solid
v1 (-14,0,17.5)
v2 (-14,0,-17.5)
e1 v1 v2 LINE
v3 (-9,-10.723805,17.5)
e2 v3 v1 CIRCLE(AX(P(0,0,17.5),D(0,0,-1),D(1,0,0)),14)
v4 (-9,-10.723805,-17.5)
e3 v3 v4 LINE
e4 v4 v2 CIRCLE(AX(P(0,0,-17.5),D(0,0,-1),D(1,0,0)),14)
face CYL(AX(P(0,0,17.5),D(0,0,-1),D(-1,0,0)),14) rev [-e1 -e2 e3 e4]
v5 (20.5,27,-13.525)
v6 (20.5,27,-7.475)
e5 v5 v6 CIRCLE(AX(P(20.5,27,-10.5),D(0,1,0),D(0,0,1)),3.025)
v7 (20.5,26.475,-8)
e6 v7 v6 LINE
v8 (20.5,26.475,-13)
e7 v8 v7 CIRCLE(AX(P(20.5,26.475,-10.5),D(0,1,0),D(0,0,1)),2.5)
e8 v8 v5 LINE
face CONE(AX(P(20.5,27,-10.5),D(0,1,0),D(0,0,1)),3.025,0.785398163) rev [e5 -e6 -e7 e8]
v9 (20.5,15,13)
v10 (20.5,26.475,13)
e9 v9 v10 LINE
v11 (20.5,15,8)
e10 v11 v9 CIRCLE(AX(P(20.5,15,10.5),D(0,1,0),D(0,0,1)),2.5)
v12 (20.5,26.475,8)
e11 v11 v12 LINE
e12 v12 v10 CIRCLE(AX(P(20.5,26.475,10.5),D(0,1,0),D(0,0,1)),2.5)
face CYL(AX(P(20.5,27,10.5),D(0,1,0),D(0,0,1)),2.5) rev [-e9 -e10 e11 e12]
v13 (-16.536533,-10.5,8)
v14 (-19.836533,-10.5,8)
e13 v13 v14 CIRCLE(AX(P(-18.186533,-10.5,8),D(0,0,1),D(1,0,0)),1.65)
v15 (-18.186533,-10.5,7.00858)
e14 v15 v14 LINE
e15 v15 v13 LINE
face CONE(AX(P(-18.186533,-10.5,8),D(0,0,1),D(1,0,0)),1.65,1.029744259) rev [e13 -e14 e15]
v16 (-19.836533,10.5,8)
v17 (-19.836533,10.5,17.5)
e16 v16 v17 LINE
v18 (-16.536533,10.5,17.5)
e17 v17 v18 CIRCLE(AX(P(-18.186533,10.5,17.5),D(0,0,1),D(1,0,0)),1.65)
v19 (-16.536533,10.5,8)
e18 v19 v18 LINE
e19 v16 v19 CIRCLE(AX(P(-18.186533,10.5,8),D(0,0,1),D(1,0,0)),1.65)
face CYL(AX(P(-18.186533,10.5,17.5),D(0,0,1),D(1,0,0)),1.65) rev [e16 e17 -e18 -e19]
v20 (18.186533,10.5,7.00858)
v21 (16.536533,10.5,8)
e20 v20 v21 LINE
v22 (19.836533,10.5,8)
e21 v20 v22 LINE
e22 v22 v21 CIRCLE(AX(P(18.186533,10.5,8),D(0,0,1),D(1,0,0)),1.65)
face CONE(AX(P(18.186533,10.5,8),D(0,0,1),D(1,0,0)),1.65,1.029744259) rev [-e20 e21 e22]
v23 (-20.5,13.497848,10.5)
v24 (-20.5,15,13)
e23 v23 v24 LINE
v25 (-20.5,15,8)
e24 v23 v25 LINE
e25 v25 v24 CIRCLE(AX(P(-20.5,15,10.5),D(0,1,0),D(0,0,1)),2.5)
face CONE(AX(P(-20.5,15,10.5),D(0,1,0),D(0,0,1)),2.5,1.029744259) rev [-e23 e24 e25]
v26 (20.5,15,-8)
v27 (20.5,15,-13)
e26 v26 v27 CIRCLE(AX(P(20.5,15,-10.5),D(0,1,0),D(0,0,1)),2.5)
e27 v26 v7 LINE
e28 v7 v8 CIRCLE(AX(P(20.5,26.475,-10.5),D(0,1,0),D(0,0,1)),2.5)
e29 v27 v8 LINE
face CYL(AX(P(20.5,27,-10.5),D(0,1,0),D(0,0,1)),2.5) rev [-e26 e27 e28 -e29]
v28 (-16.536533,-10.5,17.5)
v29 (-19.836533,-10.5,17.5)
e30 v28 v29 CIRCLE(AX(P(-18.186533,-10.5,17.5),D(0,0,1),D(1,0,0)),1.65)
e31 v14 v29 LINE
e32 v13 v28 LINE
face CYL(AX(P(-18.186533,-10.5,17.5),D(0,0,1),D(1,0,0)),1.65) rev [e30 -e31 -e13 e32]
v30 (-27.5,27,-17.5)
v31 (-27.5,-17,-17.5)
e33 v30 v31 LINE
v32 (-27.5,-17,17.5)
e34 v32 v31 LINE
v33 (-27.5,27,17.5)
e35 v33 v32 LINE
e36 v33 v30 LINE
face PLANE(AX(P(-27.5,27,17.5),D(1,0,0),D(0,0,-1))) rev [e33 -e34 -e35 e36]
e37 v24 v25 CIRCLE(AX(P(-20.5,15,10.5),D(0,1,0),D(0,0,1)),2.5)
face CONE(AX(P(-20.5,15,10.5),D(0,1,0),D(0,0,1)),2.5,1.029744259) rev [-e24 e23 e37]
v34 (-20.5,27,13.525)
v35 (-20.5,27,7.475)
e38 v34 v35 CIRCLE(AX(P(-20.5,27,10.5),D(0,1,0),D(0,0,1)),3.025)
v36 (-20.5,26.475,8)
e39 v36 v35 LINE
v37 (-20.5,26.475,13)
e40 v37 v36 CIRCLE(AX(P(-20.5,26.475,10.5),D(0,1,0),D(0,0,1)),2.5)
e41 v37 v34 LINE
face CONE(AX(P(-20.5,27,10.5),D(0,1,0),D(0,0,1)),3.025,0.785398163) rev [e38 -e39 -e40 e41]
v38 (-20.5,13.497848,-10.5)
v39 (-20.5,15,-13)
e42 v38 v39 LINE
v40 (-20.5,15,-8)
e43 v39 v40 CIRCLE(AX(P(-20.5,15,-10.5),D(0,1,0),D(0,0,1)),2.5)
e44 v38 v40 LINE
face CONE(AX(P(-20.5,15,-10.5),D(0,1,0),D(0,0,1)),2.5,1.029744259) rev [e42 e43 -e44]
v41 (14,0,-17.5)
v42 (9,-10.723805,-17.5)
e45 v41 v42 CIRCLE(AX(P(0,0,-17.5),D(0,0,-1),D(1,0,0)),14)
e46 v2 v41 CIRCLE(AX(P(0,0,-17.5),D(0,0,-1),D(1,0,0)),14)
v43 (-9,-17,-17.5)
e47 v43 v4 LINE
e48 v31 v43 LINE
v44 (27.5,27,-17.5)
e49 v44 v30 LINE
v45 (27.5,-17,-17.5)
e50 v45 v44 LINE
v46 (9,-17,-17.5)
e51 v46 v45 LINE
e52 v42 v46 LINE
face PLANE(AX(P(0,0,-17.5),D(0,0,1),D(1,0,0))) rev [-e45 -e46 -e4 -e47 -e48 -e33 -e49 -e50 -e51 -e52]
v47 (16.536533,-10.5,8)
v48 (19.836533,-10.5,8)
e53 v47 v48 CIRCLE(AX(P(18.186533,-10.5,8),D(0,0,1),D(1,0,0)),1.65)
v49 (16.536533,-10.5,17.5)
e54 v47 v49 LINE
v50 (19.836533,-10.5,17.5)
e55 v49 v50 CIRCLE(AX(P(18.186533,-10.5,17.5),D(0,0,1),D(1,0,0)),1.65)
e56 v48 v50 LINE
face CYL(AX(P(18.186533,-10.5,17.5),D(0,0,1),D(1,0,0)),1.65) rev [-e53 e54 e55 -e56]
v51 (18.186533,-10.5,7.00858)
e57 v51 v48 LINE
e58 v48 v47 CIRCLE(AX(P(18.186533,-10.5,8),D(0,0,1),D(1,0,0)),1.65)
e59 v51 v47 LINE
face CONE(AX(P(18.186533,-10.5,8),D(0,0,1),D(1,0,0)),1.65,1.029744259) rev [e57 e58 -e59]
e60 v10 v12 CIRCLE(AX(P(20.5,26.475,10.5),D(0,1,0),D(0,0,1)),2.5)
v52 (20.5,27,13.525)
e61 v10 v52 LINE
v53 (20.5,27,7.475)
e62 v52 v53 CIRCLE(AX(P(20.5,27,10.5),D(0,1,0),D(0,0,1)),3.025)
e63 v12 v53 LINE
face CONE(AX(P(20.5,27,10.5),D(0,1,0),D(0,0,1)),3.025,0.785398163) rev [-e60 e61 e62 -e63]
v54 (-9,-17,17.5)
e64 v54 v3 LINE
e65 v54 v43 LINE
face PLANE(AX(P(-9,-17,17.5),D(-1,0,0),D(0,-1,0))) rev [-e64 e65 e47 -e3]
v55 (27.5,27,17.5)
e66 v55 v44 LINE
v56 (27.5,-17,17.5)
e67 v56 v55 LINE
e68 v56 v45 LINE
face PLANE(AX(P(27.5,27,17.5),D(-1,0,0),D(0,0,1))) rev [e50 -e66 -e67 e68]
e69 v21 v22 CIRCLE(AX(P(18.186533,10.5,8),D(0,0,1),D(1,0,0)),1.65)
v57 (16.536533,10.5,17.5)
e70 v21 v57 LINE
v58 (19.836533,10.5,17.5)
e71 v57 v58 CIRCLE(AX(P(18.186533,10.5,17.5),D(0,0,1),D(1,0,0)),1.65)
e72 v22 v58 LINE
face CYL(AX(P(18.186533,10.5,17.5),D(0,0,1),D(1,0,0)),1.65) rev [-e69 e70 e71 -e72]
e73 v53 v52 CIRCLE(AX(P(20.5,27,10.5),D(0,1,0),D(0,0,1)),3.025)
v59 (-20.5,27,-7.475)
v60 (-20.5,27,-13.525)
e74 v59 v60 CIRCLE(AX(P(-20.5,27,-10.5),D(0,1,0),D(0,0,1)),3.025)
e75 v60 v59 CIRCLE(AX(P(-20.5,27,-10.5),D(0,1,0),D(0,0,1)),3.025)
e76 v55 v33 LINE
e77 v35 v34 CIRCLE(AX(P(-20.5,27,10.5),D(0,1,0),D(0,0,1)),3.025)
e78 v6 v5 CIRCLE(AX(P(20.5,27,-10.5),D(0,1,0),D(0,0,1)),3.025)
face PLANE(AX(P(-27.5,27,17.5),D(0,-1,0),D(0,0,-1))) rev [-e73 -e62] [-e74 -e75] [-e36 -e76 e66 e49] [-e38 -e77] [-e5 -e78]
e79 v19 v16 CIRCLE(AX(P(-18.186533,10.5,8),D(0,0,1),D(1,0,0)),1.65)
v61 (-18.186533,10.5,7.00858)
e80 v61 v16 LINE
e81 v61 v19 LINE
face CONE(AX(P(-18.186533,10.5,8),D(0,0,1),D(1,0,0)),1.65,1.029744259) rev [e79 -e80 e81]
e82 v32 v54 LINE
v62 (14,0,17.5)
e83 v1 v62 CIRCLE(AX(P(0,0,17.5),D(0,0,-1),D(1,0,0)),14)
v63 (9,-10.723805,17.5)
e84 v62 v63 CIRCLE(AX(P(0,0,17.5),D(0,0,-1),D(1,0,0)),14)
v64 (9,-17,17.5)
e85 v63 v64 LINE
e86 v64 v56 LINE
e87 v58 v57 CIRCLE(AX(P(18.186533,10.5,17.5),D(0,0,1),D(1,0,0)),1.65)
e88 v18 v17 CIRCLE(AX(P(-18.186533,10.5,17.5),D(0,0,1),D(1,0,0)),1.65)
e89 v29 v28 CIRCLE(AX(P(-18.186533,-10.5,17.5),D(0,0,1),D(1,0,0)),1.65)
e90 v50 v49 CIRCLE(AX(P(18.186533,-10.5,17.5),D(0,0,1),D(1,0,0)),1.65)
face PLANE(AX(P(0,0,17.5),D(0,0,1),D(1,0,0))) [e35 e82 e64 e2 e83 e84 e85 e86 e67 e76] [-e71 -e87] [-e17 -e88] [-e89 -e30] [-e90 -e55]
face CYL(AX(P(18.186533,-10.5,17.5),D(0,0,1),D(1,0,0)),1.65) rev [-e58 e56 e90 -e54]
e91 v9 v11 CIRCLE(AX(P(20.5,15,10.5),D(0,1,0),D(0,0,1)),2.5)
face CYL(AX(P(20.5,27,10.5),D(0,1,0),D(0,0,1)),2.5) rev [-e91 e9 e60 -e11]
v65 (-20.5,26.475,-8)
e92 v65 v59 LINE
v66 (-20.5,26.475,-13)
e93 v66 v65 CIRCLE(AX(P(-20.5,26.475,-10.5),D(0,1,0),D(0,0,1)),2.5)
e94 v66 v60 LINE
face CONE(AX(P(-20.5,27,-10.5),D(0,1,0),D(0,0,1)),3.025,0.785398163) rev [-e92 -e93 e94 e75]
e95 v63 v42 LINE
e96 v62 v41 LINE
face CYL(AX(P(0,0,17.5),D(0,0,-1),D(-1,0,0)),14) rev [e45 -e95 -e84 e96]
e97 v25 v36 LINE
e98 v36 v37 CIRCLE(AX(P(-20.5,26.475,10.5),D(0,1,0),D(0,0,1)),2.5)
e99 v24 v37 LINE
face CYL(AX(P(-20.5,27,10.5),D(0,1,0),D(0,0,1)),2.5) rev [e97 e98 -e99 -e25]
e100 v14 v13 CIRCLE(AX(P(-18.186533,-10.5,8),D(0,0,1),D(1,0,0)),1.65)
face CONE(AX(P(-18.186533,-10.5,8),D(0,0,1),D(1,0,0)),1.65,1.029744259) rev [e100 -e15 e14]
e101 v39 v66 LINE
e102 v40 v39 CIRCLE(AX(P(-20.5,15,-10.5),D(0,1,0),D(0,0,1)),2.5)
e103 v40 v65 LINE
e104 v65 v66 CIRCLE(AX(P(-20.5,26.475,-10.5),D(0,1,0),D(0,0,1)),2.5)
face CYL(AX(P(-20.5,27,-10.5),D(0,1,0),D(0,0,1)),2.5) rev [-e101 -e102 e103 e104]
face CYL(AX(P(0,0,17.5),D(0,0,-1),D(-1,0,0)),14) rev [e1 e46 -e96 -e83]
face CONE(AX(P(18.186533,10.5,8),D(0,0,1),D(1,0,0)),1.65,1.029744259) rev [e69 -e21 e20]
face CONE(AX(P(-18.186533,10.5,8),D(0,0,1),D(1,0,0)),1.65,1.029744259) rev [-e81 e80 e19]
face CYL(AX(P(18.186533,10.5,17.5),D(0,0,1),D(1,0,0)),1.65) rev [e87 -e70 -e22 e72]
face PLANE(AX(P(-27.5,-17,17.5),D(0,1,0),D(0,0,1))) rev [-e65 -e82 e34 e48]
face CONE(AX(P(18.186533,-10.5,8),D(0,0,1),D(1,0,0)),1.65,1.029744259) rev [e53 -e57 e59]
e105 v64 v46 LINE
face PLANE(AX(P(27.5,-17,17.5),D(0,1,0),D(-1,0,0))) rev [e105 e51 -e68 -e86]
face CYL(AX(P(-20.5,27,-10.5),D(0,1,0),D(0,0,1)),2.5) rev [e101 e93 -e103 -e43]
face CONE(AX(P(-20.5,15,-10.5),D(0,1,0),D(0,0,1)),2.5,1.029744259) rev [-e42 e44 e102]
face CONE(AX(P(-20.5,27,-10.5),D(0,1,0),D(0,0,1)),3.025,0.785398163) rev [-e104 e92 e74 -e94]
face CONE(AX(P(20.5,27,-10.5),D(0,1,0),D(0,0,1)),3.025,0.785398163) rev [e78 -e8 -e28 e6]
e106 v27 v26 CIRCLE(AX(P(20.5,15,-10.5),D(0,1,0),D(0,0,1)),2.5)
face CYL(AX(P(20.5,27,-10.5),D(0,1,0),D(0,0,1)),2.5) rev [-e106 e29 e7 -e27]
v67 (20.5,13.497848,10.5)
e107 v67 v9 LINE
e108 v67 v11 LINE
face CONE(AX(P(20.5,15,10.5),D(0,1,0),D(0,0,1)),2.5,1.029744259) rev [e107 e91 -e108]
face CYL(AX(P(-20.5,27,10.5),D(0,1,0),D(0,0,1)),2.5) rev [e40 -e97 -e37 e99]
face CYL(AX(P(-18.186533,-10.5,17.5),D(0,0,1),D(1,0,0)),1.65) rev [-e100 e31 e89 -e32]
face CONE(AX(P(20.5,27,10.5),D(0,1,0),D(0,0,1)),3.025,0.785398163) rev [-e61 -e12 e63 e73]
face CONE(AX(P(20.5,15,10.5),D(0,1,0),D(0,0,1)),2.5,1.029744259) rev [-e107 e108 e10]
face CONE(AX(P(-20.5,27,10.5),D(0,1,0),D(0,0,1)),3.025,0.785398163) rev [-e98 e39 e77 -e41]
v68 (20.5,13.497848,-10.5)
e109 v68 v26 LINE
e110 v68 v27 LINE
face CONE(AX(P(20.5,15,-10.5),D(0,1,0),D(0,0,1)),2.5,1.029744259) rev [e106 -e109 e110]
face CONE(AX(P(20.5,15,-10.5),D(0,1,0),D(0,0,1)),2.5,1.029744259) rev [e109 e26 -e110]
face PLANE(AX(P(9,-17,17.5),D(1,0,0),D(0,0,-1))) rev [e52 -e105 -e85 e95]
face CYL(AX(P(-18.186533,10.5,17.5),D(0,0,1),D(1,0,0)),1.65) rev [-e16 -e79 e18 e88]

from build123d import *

# Parameters (mm, degrees)
EXTRUDE_1_DEPTH              = 17.5
HOLE_WIZARD_M4_1_D           = 3.3
HOLE_WIZARD_M4_1_DEPTH       = 9.5
HOLE_WIZARD_M4_1_TIP         = 0.991420021
HOLE_WIZARD_M6_1_D           = 5
HOLE_WIZARD_M6_1_DEPTH       = 12
HOLE_WIZARD_M6_1_CSINK_D     = 6.05
HOLE_WIZARD_M6_1_CSINK_ANGLE = 90
HOLE_WIZARD_M6_1_TIP         = 1.502151548


with BuildPart() as part:
    # 草图1 → 凸台-拉伸1 (new, symmetric)
    with BuildSketch(Plane.XY):
        with BuildLine():
            Line((-27.5, 27), (27.5, 27))
            Line((27.5, 27), (27.5, -17))
            Line((27.5, -17), (9, -17))
            Line((9, -17), (9, -10.723805295))
            ThreePointArc((9, -10.723805295), (0, 14), (-9, -10.723805295))
            Line((-9, -10.723805295), (-9, -17))
            Line((-9, -17), (-27.5, -17))
            Line((-27.5, -17), (-27.5, 27))
        make_face()
    extrude(amount=EXTRUDE_1_DEPTH, both=True)

    # M4 螺纹孔1
    with Locations(Plane.XY.offset(17.5)):
        with Locations((18.186533479, 10.5), (18.186533479, -10.5), (-18.186533479, -10.5), (-18.186533479, 10.5)):
            Hole(HOLE_WIZARD_M4_1_D / 2, depth=HOLE_WIZARD_M4_1_DEPTH)
            with Locations((0, 0, -(HOLE_WIZARD_M4_1_DEPTH + HOLE_WIZARD_M4_1_TIP / 2))):  # 118° drill point
                Cone(0, HOLE_WIZARD_M4_1_D / 2, HOLE_WIZARD_M4_1_TIP, mode=Mode.SUBTRACT)

    # M6 螺纹孔1
    with Locations(Plane(origin=(-20.5, 27, 10.5), x_dir=(0, 0, 1), z_dir=(0, 1, 0))):
        with Locations((0, 0), (-21, 0), (-21, 41), (0, 41)):
            CounterSinkHole(HOLE_WIZARD_M6_1_D / 2, HOLE_WIZARD_M6_1_CSINK_D / 2, depth=HOLE_WIZARD_M6_1_DEPTH, counter_sink_angle=HOLE_WIZARD_M6_1_CSINK_ANGLE)
            with Locations((0, 0, -(HOLE_WIZARD_M6_1_DEPTH + HOLE_WIZARD_M6_1_TIP / 2))):  # 118° drill point
                Cone(0, HOLE_WIZARD_M6_1_D / 2, HOLE_WIZARD_M6_1_TIP, mode=Mode.SUBTRACT)


solid = part.part
